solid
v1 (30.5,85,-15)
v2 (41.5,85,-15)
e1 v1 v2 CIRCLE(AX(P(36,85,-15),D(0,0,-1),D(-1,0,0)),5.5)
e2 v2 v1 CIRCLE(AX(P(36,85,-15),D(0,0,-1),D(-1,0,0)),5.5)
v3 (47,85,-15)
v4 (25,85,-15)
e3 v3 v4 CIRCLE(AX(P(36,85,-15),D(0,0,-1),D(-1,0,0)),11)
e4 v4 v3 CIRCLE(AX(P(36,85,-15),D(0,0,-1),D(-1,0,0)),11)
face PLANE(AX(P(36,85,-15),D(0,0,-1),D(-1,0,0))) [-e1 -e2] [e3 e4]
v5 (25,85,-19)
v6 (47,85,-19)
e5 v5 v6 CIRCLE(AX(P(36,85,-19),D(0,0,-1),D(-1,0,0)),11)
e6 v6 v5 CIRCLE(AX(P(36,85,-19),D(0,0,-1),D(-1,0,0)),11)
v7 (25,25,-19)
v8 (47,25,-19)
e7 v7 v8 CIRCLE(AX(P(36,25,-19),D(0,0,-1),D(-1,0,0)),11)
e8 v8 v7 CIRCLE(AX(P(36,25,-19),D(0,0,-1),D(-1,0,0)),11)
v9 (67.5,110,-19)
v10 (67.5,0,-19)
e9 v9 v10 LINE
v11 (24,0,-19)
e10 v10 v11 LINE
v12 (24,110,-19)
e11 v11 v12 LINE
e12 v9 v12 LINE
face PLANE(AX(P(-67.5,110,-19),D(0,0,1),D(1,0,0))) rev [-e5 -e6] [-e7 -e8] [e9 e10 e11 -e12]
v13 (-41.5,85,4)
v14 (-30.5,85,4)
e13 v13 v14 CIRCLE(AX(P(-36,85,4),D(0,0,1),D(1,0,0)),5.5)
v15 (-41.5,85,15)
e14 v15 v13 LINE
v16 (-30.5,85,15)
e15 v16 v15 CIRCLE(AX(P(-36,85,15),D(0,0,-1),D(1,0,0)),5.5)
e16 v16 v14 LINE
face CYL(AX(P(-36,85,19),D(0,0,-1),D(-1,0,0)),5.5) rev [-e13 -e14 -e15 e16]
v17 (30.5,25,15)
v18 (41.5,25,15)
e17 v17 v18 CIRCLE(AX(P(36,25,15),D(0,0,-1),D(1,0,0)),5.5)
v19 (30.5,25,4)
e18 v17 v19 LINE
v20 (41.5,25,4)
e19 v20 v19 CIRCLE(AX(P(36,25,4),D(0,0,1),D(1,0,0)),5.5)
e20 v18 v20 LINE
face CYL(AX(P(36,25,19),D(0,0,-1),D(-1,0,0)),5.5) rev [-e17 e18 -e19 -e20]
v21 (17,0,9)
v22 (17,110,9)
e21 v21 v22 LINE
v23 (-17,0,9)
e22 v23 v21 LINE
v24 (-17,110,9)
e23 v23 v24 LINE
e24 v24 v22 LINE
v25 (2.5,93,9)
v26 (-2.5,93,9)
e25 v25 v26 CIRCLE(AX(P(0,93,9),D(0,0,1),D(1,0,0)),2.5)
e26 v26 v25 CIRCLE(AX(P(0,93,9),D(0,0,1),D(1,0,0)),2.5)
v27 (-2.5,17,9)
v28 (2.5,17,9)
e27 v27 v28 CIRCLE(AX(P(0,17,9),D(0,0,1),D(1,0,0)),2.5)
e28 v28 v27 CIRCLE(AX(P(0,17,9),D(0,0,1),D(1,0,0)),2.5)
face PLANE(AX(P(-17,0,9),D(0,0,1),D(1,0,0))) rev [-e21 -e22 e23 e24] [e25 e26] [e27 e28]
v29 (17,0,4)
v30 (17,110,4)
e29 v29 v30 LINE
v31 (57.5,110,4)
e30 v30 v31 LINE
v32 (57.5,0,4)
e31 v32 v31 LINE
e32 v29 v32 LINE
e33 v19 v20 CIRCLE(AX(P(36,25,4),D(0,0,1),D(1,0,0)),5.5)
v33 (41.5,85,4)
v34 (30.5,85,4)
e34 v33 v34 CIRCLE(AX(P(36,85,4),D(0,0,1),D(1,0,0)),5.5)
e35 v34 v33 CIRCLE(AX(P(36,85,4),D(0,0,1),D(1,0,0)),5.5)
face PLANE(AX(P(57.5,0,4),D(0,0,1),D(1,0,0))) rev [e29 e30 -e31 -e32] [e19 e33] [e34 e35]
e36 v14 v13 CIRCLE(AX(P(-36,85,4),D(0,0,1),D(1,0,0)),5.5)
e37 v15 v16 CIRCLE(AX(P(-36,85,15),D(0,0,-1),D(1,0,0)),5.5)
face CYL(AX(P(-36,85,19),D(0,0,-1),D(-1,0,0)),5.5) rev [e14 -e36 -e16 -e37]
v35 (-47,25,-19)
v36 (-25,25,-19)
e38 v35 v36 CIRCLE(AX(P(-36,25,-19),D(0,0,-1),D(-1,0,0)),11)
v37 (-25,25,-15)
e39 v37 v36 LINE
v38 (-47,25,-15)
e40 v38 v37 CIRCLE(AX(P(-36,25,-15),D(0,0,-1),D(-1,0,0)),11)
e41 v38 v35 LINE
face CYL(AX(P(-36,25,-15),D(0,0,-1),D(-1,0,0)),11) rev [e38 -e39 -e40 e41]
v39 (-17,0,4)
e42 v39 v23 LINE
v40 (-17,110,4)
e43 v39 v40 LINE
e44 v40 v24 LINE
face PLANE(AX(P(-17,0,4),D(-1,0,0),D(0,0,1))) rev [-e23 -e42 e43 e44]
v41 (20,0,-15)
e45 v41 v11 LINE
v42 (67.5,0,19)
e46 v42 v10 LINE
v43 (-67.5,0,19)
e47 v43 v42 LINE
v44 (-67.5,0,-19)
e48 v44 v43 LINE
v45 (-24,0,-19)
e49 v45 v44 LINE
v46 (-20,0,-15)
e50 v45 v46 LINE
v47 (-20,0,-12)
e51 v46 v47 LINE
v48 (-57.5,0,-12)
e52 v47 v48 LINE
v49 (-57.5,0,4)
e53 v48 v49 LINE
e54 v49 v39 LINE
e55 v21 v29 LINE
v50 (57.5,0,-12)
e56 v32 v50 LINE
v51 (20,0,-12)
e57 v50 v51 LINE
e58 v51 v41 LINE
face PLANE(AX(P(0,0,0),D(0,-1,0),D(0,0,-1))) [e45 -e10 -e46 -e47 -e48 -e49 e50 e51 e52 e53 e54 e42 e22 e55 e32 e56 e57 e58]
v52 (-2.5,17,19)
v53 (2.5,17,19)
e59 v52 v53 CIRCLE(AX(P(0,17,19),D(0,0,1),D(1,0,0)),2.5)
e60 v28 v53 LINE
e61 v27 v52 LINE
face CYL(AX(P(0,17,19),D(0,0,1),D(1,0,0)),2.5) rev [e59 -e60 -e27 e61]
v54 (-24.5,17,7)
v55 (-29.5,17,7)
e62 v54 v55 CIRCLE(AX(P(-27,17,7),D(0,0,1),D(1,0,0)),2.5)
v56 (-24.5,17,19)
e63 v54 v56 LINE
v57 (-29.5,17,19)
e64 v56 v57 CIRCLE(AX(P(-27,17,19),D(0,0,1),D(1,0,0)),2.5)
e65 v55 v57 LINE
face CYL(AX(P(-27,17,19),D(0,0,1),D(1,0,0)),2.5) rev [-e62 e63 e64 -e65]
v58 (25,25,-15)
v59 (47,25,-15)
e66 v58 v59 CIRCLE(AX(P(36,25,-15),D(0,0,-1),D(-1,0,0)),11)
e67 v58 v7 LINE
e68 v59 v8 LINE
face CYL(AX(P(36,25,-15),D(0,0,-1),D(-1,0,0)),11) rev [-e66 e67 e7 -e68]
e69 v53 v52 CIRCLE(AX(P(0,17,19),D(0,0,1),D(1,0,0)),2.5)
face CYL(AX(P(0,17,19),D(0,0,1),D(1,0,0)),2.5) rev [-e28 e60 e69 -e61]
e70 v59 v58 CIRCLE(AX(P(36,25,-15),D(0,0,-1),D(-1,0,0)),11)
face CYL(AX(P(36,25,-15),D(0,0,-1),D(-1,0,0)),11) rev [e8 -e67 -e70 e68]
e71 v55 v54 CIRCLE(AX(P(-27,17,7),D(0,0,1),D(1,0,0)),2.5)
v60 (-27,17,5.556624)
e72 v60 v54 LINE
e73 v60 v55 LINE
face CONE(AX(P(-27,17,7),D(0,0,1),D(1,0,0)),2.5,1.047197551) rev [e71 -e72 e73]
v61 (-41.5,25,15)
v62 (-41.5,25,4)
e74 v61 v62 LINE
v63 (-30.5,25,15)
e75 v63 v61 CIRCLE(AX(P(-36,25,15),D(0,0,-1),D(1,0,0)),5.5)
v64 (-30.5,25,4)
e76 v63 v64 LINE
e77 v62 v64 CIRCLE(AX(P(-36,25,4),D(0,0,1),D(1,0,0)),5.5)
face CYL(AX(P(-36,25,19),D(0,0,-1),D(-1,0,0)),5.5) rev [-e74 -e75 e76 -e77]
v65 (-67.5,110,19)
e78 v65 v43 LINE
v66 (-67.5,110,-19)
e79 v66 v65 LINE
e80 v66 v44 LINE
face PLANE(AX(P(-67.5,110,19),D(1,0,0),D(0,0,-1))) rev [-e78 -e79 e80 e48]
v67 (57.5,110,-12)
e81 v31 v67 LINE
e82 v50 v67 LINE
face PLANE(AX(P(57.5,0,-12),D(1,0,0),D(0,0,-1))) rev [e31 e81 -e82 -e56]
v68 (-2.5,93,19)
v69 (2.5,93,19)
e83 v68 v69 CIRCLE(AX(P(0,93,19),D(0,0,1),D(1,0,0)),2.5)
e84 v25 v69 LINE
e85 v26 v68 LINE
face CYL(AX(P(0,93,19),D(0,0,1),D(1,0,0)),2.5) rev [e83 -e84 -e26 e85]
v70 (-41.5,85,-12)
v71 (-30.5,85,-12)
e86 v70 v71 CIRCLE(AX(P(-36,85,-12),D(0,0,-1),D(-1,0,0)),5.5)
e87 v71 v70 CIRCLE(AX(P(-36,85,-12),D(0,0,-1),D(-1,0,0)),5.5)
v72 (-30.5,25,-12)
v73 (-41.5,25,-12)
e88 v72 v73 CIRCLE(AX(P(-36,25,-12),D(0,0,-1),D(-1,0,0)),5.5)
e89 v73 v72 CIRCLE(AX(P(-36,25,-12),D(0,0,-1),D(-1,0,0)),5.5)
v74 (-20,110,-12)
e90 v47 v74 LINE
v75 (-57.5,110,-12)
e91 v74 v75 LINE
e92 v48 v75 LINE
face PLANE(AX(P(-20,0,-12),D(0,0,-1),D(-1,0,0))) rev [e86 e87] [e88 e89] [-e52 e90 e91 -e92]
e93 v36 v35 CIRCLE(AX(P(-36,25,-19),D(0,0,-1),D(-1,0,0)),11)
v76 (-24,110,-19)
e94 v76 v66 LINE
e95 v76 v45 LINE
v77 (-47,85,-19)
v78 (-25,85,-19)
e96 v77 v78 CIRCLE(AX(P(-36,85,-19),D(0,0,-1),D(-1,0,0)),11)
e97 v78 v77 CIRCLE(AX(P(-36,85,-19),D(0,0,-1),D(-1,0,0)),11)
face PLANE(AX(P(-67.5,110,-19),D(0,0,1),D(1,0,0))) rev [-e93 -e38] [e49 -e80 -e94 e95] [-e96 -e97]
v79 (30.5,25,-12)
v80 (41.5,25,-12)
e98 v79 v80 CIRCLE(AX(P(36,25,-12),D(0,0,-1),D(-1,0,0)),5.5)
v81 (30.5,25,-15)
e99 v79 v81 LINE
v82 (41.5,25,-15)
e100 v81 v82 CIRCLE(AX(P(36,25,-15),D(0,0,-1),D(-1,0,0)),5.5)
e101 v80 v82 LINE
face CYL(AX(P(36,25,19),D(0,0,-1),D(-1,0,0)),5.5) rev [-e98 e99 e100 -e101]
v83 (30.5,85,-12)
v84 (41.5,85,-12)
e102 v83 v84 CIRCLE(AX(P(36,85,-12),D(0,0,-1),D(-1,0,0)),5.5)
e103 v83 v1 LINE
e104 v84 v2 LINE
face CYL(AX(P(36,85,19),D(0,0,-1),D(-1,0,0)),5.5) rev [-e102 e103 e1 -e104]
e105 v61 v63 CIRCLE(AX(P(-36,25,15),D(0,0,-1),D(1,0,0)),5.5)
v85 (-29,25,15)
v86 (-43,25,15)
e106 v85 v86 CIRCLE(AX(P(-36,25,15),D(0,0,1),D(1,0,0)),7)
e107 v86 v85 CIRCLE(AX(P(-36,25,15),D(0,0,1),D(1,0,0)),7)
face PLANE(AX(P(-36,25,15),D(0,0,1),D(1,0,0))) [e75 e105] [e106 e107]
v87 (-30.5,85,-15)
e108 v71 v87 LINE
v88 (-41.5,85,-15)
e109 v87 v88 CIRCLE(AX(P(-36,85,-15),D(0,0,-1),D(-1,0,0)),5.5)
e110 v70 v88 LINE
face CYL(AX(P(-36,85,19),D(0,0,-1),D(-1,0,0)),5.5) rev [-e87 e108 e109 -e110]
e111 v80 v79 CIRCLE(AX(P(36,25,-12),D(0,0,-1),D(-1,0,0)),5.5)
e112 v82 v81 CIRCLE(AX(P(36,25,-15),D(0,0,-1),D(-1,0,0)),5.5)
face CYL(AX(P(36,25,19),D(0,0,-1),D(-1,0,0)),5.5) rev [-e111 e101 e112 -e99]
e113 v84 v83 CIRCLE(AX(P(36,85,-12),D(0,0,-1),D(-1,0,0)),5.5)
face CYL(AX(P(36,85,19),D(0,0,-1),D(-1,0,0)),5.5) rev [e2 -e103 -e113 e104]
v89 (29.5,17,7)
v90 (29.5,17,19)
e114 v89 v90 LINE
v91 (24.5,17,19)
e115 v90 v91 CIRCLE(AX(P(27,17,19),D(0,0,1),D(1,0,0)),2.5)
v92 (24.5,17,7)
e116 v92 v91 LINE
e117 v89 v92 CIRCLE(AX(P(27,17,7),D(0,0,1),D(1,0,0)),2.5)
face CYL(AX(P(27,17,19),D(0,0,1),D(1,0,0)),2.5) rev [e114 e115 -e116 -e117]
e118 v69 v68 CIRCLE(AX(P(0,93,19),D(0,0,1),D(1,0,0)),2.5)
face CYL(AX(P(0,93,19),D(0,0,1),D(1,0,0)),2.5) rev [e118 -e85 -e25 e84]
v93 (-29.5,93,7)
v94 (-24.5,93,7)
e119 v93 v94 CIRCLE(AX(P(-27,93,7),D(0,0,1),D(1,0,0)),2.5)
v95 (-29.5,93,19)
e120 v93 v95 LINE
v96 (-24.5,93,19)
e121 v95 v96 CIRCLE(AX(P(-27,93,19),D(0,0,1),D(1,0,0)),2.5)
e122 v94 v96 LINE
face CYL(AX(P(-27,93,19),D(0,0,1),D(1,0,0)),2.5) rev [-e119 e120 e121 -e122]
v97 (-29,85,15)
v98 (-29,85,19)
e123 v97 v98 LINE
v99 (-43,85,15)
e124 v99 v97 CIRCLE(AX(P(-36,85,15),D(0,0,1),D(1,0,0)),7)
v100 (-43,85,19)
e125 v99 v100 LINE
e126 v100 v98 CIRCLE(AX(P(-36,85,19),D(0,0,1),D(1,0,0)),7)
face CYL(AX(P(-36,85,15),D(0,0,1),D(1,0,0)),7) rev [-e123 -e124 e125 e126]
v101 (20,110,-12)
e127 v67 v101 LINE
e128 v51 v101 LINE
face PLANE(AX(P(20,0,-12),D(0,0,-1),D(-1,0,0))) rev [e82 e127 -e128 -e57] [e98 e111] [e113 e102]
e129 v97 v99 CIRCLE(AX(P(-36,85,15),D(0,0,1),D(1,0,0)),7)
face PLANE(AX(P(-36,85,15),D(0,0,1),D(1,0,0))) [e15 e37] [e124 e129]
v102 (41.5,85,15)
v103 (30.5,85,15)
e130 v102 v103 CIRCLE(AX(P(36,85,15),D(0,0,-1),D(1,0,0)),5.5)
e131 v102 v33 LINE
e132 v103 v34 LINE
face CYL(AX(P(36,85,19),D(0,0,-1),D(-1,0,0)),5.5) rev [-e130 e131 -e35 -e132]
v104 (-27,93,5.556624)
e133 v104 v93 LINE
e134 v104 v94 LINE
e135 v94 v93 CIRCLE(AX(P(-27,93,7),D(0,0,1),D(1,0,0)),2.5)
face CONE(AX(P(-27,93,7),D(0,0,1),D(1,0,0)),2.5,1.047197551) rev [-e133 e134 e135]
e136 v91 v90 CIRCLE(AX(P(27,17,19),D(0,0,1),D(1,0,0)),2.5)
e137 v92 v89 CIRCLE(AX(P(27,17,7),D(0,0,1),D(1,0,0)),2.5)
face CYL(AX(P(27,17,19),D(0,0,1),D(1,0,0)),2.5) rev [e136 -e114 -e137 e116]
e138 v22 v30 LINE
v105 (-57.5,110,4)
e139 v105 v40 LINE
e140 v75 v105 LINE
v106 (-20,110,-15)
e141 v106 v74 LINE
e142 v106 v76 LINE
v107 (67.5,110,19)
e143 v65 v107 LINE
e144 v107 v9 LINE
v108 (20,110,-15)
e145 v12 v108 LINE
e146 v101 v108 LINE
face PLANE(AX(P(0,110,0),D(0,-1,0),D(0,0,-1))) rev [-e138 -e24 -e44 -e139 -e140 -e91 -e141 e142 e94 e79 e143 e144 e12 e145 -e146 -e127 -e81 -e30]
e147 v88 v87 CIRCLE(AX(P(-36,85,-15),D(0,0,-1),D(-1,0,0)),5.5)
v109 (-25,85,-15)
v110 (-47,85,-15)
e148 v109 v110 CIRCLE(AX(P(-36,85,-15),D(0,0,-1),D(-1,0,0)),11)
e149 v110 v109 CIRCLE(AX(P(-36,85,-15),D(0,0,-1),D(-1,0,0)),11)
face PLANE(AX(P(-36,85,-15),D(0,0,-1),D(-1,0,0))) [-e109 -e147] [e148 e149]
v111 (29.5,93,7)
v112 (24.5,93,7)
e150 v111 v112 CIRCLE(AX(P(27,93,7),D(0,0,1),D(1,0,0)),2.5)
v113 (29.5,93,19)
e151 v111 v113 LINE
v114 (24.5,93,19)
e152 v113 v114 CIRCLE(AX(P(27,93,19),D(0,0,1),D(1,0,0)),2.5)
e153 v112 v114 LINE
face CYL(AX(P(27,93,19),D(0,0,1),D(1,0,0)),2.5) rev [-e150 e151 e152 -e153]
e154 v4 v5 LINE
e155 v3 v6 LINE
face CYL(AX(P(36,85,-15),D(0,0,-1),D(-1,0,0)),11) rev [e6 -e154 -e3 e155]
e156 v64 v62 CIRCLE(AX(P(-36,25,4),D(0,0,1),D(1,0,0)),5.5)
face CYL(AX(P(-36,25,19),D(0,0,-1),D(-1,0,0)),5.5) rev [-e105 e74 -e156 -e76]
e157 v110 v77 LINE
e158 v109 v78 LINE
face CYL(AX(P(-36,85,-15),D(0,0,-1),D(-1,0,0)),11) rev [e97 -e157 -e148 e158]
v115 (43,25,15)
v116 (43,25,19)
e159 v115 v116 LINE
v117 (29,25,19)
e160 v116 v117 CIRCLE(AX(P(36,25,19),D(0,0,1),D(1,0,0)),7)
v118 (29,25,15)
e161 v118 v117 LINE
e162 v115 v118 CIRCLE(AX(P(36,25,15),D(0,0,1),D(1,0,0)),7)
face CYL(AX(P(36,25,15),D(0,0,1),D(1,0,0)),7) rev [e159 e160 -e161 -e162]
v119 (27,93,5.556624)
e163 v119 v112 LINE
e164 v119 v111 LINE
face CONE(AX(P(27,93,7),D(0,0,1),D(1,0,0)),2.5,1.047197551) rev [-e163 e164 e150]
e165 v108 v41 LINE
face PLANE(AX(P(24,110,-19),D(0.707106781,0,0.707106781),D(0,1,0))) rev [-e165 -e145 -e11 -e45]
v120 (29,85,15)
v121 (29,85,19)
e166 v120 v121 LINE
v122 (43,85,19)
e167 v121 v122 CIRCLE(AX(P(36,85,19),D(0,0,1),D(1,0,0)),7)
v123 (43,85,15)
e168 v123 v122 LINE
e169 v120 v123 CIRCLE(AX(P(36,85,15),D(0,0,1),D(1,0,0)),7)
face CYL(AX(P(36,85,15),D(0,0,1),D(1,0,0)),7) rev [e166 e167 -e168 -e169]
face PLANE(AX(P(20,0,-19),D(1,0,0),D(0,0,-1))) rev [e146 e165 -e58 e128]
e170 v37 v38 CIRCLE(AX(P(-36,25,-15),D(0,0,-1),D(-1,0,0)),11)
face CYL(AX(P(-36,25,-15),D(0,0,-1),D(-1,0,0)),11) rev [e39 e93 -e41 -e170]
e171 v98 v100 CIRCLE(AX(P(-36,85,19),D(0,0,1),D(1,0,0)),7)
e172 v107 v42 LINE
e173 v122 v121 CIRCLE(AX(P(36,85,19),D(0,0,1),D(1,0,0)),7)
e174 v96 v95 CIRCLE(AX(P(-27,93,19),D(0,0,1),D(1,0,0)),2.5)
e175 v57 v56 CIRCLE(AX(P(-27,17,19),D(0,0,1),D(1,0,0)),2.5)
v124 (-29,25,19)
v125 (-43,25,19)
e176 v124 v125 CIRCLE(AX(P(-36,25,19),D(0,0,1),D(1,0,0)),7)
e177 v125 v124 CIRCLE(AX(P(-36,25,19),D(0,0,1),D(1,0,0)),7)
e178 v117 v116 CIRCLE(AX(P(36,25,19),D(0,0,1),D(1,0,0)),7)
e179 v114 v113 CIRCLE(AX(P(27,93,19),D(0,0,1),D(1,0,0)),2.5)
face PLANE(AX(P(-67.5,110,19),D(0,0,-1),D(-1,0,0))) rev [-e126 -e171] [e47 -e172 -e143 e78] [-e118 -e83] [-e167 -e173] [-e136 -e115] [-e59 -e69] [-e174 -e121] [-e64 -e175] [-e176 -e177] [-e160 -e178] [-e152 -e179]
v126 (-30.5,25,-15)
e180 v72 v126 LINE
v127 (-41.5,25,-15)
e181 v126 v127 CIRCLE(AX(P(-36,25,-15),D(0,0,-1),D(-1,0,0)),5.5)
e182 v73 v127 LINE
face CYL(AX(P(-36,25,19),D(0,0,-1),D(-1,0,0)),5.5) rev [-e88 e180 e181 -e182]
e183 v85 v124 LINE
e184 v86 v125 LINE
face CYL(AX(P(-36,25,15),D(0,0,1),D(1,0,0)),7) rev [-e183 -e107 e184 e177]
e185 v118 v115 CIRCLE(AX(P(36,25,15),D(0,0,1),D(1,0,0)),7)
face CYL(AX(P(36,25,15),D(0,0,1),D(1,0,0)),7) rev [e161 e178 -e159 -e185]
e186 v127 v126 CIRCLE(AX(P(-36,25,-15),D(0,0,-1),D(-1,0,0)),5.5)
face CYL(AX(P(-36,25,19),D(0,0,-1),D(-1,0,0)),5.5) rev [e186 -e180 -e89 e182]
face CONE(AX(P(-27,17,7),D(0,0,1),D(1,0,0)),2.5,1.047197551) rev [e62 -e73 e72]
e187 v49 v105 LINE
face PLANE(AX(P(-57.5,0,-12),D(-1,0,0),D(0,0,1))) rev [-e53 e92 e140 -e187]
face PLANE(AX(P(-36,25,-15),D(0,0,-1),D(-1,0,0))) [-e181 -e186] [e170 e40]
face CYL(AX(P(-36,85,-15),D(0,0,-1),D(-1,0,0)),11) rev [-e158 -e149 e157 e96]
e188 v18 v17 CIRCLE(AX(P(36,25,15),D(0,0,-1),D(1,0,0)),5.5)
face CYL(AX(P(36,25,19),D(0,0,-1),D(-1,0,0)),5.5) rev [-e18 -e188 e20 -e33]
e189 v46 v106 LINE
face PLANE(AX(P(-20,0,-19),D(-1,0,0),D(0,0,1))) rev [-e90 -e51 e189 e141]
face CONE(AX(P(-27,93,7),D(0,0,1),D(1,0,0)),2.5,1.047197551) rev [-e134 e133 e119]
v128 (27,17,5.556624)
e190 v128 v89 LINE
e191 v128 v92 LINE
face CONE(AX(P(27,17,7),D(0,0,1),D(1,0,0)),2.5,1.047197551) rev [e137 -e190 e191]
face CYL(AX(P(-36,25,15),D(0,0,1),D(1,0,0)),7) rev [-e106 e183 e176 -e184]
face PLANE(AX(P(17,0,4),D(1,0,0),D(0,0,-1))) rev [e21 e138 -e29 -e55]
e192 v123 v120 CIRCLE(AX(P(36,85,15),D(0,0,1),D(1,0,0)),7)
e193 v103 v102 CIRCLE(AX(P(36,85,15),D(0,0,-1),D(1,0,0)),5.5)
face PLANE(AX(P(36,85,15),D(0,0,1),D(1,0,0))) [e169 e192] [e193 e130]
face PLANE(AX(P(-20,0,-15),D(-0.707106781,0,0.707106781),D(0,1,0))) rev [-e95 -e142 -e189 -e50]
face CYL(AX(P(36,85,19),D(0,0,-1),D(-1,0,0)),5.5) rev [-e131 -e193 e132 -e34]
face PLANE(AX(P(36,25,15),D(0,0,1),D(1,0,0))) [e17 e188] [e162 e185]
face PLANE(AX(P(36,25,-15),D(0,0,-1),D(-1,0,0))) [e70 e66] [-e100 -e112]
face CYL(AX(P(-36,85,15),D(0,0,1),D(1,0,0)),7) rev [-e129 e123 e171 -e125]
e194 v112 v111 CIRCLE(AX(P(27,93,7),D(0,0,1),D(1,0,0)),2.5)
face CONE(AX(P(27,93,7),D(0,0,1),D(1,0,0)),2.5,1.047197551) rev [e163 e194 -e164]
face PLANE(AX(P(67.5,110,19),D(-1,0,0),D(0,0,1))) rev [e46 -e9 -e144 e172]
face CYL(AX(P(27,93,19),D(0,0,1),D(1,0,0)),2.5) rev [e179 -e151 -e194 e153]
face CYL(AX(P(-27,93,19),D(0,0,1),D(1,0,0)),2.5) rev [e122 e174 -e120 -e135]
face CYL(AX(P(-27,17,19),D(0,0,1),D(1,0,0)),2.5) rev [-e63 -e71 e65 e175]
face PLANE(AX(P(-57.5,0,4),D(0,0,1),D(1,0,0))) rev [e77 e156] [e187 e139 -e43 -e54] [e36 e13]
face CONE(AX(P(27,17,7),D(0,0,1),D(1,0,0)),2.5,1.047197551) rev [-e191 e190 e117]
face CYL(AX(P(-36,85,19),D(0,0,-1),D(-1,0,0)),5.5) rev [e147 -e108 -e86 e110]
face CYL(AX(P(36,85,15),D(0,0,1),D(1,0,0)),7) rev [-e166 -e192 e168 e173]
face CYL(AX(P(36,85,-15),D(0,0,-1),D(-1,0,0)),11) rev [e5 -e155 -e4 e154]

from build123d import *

# Parameters (mm, degrees)
SKETCH_1_W                  = 135
SKETCH_1_H                  = 38
EXTRUDE_1_DEPTH             = 110
CUT_EXTRUDE_1_DEPTH         = 131.450182062
SKETCH_4_R                  = 11
CUT_EXTRUDE_2_DEPTH         = 4
SKETCH_5_R                  = 5.5
CUT_EXTRUDE_3_DEPTH         = 134.462541561
SKETCH_6_R                  = 7
CUT_EXTRUDE_4_DEPTH         = 4
PATTERN_LINEAR_1_COUNT      = 2
PATTERN_LINEAR_1_PITCH      = 60
PATTERN_LINEAR_1_COUNT_DIR2 = 2
PATTERN_LINEAR_1_PITCH_DIR2 = 72
PATTERN_LINEAR_2_COUNT      = 3
PATTERN_LINEAR_2_PITCH      = 27
PATTERN_LINEAR_2_COUNT_DIR2 = 2
PATTERN_LINEAR_2_PITCH_DIR2 = 76
CHAMFER_1_SIZE              = 4


with BuildPart() as part:
    # 草图1 → 凸台-拉伸1 (new body)
    with BuildSketch(Plane(origin=(0, 0, 0), x_dir=(1, 0, 0), z_dir=(0, 1, 0))):
        Rectangle(SKETCH_1_W, SKETCH_1_H)
    extrude(amount=EXTRUDE_1_DEPTH)

    # 草图3 → 切除-拉伸1 (cut, through all)
    with BuildSketch(Plane(origin=(0, 110, 0), x_dir=(1, 0, 0), z_dir=(0, 1, 0))):
        Polygon((20, 19), (-20, 19), (-20, 12), (-57.5, 12), (-57.5, -4), (-17, -4), (-17, -9), (17, -9), (17, -4), (57.5, -4), (57.5, 12), (20, 12), align=None)
    extrude(amount=-CUT_EXTRUDE_1_DEPTH, mode=Mode.SUBTRACT)

    # 草图4 → 切除-拉伸2 (cut)
    with BuildSketch(Plane(origin=(0, 0, -19), x_dir=(-1, 0, 0), z_dir=(0, 0, -1))):
        with Locations((-36, 85)):
            Circle(SKETCH_4_R)
    cut_extrude_2 = extrude(amount=-CUT_EXTRUDE_2_DEPTH, mode=Mode.SUBTRACT)

    # 草图5 → 切除-拉伸3 (cut, through all)
    with BuildSketch(Plane(origin=(0, 0, -15), x_dir=(-1, 0, 0), z_dir=(0, 0, -1))):
        with Locations((-36, 85)):
            Circle(SKETCH_5_R)
    cut_extrude_3 = extrude(amount=-CUT_EXTRUDE_3_DEPTH, mode=Mode.SUBTRACT)

    # 草图6 → 切除-拉伸4 (cut)
    with BuildSketch(Plane.XY.offset(19)):
        with Locations((36, 85)):
            Circle(SKETCH_6_R)
    cut_extrude_4 = extrude(amount=-CUT_EXTRUDE_4_DEPTH, mode=Mode.SUBTRACT)

    # 阵列(线性)1: 切除-拉伸2, 切除-拉伸3, Cut-Extrude 4 2 × 2
    with Locations(*[(-j * PATTERN_LINEAR_1_PITCH_DIR2, -i * PATTERN_LINEAR_1_PITCH, 0) for i in range(PATTERN_LINEAR_1_COUNT) for j in range(PATTERN_LINEAR_1_COUNT_DIR2) if (i, j) != (0, 0)]):
        add(cut_extrude_2, mode=Mode.SUBTRACT)
        add(cut_extrude_3, mode=Mode.SUBTRACT)
        add(cut_extrude_4, mode=Mode.SUBTRACT)

    # 草图7 → M6 螺纹孔1 (revolve, cut)
    with BuildSketch(Plane(origin=(27, 93, 19), x_dir=(0, -1, 0), z_dir=(1, 0, 0))):
        Polygon((0, 0), (0, 13.443375673), (2.5, 12), (2.5, 0), align=None)
    hole_wizard_m6_1 = revolve(axis=Axis((27, 93, 25.35), (0, 0, -1)), mode=Mode.SUBTRACT)

    # 阵列(线性)2: Hole Wizard M6 _1 3 × 2
    with Locations(*[(-i * PATTERN_LINEAR_2_PITCH, -j * PATTERN_LINEAR_2_PITCH_DIR2, 0) for i in range(PATTERN_LINEAR_2_COUNT) for j in range(PATTERN_LINEAR_2_COUNT_DIR2) if (i, j) != (0, 0)]):
        add(hole_wizard_m6_1, mode=Mode.SUBTRACT)

    # 倒角1
    chamfer_1_edges = [part.edges().sort_by_distance(p)[0] for p in [
        (-20, 55, -19),
        (20, 55, -19),
    ]]
    chamfer(chamfer_1_edges, length=CHAMFER_1_SIZE)


solid = part.part
